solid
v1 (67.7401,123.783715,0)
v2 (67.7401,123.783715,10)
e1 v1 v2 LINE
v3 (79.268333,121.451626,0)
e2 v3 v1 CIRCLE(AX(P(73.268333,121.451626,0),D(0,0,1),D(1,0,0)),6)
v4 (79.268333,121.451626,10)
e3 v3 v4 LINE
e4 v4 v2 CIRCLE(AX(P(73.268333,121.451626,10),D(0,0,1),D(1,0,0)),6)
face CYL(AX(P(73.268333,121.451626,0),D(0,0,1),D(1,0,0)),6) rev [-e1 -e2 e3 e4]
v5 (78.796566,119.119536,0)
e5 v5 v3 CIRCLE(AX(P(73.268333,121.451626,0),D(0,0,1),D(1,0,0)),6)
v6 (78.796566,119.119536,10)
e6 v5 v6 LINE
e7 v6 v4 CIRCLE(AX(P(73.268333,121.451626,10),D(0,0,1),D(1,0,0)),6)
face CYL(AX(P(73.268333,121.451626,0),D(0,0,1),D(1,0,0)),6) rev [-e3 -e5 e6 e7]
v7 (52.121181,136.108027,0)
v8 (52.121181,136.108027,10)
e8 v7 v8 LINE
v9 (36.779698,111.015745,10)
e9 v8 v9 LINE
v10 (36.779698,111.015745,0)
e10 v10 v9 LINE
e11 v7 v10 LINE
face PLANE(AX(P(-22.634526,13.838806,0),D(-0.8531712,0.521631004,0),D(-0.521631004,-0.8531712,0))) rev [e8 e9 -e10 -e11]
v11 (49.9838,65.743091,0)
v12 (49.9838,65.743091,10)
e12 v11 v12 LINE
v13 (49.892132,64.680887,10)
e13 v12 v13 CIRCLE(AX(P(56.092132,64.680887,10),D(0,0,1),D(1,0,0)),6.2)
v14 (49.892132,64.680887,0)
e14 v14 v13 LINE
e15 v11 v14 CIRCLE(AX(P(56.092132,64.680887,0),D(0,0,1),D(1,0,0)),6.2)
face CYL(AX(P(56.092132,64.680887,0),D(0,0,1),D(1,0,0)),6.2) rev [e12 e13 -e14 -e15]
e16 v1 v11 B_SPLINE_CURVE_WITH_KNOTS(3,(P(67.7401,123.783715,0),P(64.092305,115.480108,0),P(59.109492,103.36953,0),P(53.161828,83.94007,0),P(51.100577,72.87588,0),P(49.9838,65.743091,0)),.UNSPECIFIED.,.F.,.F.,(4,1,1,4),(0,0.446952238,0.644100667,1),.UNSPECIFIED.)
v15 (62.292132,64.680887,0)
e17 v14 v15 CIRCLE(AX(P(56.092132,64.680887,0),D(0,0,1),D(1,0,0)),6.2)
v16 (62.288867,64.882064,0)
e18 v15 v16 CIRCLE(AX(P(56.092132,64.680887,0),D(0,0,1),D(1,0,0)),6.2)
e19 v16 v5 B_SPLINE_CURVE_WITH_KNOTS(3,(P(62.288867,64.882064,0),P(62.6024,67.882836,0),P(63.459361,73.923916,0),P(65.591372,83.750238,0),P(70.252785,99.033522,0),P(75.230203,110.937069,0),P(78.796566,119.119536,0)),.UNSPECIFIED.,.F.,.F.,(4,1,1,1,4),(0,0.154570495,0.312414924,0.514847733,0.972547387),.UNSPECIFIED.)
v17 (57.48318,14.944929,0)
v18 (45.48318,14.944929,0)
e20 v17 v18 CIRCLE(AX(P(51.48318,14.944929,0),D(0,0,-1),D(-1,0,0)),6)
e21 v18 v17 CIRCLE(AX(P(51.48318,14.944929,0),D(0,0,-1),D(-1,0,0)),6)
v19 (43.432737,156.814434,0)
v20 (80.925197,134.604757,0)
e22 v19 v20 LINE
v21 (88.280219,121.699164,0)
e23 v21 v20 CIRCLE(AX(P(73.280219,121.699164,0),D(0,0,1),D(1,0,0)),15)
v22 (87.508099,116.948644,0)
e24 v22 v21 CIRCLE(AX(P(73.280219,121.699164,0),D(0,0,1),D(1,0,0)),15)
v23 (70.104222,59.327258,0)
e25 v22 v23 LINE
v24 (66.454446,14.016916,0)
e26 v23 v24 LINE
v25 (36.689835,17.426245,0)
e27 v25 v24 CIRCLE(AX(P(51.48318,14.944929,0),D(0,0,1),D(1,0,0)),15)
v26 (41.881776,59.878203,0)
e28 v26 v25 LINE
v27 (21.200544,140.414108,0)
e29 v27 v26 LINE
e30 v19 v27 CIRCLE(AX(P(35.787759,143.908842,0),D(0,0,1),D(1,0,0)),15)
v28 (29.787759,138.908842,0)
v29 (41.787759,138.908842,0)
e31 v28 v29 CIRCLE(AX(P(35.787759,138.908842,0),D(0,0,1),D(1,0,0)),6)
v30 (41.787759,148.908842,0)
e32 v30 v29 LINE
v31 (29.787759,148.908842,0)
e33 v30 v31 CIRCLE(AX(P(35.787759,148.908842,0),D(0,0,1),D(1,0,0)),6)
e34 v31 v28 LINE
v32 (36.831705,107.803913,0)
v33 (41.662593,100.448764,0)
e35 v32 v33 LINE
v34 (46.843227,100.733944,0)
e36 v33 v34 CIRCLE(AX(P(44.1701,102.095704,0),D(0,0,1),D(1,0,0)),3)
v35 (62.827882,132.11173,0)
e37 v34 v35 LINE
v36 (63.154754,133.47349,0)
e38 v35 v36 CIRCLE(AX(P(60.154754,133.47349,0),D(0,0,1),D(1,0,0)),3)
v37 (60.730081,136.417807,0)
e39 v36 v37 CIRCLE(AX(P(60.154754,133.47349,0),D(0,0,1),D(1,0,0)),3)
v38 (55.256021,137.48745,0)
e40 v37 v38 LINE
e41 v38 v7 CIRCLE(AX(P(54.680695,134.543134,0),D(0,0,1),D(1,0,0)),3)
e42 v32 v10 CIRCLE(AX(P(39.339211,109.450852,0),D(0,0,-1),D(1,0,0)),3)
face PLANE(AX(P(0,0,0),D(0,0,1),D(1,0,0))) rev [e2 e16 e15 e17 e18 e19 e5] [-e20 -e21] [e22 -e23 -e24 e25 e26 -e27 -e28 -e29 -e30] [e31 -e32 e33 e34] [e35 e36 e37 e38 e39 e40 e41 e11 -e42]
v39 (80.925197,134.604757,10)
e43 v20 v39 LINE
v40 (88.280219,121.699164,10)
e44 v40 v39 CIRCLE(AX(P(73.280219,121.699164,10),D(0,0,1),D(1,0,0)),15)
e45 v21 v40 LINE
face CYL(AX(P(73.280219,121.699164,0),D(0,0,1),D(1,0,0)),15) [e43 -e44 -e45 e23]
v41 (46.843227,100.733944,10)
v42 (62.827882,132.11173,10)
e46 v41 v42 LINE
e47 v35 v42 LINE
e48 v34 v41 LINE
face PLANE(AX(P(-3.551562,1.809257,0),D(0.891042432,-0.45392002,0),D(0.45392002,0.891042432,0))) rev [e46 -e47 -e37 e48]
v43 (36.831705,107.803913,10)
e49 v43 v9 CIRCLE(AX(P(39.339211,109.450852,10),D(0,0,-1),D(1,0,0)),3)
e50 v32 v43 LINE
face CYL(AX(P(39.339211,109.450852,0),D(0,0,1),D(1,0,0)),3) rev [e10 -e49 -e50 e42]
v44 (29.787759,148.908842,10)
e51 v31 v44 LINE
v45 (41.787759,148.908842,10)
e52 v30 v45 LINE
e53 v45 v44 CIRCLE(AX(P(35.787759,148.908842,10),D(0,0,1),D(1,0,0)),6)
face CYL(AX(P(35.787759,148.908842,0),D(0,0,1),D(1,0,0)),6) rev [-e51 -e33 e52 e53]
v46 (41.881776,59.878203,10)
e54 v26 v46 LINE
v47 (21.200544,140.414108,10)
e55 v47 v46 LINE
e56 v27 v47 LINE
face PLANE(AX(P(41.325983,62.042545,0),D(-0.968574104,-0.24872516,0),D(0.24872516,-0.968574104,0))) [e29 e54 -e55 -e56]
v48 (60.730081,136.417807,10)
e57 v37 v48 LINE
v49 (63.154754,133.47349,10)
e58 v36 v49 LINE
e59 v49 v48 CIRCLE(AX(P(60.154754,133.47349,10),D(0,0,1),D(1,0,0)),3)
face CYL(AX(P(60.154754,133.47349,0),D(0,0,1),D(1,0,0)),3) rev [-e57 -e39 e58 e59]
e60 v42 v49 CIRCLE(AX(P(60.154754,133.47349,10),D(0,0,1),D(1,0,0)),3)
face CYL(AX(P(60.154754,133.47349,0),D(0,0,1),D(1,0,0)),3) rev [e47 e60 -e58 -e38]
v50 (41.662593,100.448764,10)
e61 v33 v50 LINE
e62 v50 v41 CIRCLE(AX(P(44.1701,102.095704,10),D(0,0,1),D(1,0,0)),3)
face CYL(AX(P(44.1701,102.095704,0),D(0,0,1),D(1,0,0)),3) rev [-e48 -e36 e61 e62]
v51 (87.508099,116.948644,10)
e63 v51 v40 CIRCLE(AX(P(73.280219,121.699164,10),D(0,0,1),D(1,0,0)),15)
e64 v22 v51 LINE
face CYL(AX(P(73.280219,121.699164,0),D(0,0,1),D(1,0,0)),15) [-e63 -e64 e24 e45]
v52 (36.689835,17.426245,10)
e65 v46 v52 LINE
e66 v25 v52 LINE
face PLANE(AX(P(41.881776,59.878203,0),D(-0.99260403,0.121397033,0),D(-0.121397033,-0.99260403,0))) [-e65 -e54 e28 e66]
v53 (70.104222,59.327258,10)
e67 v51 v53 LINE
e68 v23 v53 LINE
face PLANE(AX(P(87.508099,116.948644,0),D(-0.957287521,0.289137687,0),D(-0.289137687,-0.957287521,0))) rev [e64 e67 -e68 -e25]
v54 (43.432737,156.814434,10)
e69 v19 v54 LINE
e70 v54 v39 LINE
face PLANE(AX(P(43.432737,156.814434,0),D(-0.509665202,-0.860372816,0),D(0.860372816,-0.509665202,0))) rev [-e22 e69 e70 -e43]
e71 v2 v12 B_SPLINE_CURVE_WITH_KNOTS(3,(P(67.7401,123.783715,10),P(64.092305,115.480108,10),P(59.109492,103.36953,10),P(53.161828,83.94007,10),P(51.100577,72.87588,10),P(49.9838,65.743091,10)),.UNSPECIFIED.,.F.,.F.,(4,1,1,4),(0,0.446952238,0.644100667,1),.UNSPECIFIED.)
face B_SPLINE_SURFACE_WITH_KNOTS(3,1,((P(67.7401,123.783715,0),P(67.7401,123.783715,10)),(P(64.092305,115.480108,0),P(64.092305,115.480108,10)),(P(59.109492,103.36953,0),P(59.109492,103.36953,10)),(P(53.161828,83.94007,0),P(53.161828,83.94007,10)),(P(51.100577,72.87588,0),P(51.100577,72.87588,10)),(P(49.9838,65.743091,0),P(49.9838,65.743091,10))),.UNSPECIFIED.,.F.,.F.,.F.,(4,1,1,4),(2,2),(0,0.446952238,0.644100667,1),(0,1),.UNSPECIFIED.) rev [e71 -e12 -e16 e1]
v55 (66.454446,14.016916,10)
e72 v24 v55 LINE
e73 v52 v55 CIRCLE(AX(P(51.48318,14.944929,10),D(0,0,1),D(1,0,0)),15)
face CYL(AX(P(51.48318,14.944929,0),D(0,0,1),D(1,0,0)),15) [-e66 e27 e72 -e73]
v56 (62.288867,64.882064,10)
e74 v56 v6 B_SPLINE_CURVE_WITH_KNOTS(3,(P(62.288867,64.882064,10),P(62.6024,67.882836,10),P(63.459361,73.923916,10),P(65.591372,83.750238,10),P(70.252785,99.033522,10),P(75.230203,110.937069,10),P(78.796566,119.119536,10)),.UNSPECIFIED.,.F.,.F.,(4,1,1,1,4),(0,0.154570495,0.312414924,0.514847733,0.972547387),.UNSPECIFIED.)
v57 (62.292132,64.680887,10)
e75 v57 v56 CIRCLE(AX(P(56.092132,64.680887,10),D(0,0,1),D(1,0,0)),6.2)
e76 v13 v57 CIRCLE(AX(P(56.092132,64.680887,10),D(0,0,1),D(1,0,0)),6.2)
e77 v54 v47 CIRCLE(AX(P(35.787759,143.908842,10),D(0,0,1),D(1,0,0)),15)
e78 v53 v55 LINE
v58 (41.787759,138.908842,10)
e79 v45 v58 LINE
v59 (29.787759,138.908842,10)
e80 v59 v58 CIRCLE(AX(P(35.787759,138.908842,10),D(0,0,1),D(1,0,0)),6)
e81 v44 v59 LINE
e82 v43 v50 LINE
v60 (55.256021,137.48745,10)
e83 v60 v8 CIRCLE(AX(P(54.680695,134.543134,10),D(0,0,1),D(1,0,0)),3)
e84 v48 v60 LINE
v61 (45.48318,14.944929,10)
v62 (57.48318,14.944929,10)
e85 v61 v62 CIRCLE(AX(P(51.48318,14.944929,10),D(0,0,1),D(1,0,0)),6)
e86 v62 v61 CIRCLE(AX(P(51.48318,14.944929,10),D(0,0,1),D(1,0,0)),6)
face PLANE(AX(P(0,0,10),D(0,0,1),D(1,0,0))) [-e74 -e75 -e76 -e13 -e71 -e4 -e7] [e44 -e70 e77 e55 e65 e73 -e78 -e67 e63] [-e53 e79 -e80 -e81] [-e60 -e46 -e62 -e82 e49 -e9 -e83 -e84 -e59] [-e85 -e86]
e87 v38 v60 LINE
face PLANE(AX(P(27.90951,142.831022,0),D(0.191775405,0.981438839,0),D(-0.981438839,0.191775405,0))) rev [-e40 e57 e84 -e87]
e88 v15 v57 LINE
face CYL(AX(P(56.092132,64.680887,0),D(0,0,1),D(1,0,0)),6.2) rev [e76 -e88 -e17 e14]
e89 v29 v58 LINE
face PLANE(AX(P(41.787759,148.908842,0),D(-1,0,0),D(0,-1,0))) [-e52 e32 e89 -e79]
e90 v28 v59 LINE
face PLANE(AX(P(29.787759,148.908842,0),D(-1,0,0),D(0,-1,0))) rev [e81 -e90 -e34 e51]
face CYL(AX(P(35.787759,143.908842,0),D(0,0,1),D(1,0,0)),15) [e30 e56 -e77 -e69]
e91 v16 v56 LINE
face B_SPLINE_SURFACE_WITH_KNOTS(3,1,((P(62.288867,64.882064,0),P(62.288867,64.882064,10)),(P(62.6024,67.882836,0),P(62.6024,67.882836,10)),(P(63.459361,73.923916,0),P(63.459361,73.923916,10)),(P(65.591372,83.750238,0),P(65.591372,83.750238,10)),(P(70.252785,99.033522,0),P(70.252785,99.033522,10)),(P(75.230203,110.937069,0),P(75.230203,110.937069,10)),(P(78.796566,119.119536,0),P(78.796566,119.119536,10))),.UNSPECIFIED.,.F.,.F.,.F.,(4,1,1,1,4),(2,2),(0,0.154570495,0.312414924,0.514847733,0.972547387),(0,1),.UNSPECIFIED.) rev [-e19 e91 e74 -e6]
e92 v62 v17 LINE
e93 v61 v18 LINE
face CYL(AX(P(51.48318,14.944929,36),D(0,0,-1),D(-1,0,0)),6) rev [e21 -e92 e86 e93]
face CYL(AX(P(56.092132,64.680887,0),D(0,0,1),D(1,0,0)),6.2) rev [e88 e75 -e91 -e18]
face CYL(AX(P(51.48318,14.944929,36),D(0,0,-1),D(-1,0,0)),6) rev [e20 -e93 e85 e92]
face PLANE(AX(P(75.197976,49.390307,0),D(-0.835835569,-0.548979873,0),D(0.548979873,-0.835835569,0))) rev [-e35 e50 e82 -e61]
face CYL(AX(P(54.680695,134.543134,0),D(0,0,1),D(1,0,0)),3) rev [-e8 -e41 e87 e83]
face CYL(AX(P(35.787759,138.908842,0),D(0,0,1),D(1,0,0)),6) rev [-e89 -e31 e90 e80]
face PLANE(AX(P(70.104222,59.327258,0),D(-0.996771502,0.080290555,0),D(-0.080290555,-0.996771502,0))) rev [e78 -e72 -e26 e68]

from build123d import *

# Parameters (mm, degrees)
BOSS_EXTRUDE1_DEPTH = 10
CUT_EXTRUDE8_DEPTH  = 10
SKETCH21_R          = 6
CUT_EXTRUDE14_DEPTH = 36
CUT_EXTRUDE15_DEPTH = 10
SKETCH19_R          = 125.517206862
CUT_EXTRUDE16_DEPTH = 10


with BuildPart() as part:
    # Sketch1 → Boss-Extrude1 (new body)
    with BuildSketch(Plane.XY):
        Polygon((0, 0), (0, 170), (100, 170), (100, 0), (100, -20), (0, -20), align=None)
    extrude(amount=BOSS_EXTRUDE1_DEPTH)

    # Sketch9 → Cut-Extrude8 (cut)
    with BuildSketch(Plane.XY.offset(10)):
        with BuildLine():
            Line((29.787758795, 148.908841534), (29.787758795, 138.908841534))
            ThreePointArc((29.787758795, 138.908841534), (35.787758795, 132.908841534), (41.787758795, 138.908841534))
            Line((41.787758795, 138.908841534), (41.787758795, 148.908841534))
            ThreePointArc((41.787758795, 148.908841534), (35.787758795, 154.908841534), (29.787758795, 148.908841534))
        make_face()
    extrude(amount=-CUT_EXTRUDE8_DEPTH, mode=Mode.SUBTRACT)

    # Sketch21 → Cut-Extrude14 (cut)
    with BuildSketch(Plane(origin=(0, 0, 0), x_dir=(-1, 0, 0), z_dir=(0, 0, -1))):
        with Locations((-51.483180233, 14.944928588)):
            Circle(SKETCH21_R)
        with Locations((-173.125589471, 5.899139524)):
            Circle(SKETCH21_R)
    extrude(amount=-CUT_EXTRUDE14_DEPTH, mode=Mode.SUBTRACT)

    # Sketch28 → Cut-Extrude15 (cut)
    with BuildSketch(Plane.XY.offset(10)):
        with BuildLine():
            ThreePointArc((78.796565751, 119.119536449), (75.600421883, 126.979858603), (67.740099728, 123.783714736))
            add(Edge.make_bspline(
                [(67.740099728, 123.783714736), (64.092305086, 115.480107597), (59.109492341, 103.369529902), (53.161827647, 83.940069885), (51.100576539, 72.87588046), (49.983799811, 65.743090583)],
                knots=[0, 0, 0, 0, 0.446952238, 0.644100667, 1, 1, 1, 1], degree=3))
            ThreePointArc((49.983799811, 65.743090583), (55.659355828, 58.49601037), (62.288867459, 64.882064178))
            add(Edge.make_bspline(
                [(78.796565751, 119.119536449), (75.230202559, 110.937069208), (70.252785241, 99.033521906), (65.59137225, 83.75023837), (63.459360665, 73.923916137), (62.602399905, 67.882836475), (62.288867459, 64.882064178)],
                knots=[0, 0, 0, 0, 0.457699653, 0.660132463, 0.817976892, 0.972547387, 0.972547387, 0.972547387, 0.972547387], degree=3))
        make_face()
    extrude(amount=-CUT_EXTRUDE15_DEPTH, mode=Mode.SUBTRACT)

    # Sketch19 → Cut-Extrude16 (cut)
    # profile 1 of 2: a face of its own
    with BuildSketch(Plane.XY.offset(10)):
        with Locations((58.773015823, 71.241859079)):
            Circle(SKETCH19_R)
        with BuildLine():
            Line((41.881776011, 59.878203095), (36.689834848, 17.426245238))
            ThreePointArc((36.689834848, 17.426245238), (49.776196121, 0.042371585), (66.454445821, 14.016916355))
            Line((66.454445821, 14.016916355), (70.10422157, 59.327257721))
            Line((70.10422157, 59.327257721), (70.725023214, 61.382630275))
            Line((70.725023214, 61.382630275), (87.508098537, 116.948643541))
            ThreePointArc((87.508098537, 116.948643541), (87.335113551, 126.939388183), (80.925197211, 134.604756721))
            Line((80.925197211, 134.604756721), (43.432736819, 156.814433772))
            ThreePointArc((43.432736819, 156.814433772), (26.883190667, 155.979826019), (21.200543901, 140.414108121))
            Line((21.200543901, 140.414108121), (41.325983429, 62.042545062))
            Line((41.325983429, 62.042545062), (41.881776011, 59.878203095))
        make_face(mode=Mode.SUBTRACT)
    # profile 2 of 2: a face of its own
    with BuildSketch(Plane.XY.offset(10)):
        with BuildLine():
            Line((52.121181326, 136.108026927), (36.779697673, 111.015745375))
            ThreePointArc((36.779697673, 111.015745375), (36.33960448, 109.402281892), (36.831704565, 107.803912744))
            Line((36.831704565, 107.803912744), (41.662593186, 100.448764157))
            ThreePointArc((41.662593186, 100.448764157), (44.33499195, 99.10023877), (46.84322719, 100.733943719))
            Line((46.84322719, 100.733943719), (62.827881658, 132.111730058))
            ThreePointArc((62.827881658, 132.111730058), (62.851731636, 134.787382647), (60.730080577, 136.417806633))
            Line((60.730080577, 136.417806633), (55.25602114, 137.487450431))
            ThreePointArc((55.25602114, 137.487450431), (53.472410109, 137.289048664), (52.121181326, 136.108026927))
        make_face()
    extrude(amount=-CUT_EXTRUDE16_DEPTH, mode=Mode.SUBTRACT)


solid = part.part
